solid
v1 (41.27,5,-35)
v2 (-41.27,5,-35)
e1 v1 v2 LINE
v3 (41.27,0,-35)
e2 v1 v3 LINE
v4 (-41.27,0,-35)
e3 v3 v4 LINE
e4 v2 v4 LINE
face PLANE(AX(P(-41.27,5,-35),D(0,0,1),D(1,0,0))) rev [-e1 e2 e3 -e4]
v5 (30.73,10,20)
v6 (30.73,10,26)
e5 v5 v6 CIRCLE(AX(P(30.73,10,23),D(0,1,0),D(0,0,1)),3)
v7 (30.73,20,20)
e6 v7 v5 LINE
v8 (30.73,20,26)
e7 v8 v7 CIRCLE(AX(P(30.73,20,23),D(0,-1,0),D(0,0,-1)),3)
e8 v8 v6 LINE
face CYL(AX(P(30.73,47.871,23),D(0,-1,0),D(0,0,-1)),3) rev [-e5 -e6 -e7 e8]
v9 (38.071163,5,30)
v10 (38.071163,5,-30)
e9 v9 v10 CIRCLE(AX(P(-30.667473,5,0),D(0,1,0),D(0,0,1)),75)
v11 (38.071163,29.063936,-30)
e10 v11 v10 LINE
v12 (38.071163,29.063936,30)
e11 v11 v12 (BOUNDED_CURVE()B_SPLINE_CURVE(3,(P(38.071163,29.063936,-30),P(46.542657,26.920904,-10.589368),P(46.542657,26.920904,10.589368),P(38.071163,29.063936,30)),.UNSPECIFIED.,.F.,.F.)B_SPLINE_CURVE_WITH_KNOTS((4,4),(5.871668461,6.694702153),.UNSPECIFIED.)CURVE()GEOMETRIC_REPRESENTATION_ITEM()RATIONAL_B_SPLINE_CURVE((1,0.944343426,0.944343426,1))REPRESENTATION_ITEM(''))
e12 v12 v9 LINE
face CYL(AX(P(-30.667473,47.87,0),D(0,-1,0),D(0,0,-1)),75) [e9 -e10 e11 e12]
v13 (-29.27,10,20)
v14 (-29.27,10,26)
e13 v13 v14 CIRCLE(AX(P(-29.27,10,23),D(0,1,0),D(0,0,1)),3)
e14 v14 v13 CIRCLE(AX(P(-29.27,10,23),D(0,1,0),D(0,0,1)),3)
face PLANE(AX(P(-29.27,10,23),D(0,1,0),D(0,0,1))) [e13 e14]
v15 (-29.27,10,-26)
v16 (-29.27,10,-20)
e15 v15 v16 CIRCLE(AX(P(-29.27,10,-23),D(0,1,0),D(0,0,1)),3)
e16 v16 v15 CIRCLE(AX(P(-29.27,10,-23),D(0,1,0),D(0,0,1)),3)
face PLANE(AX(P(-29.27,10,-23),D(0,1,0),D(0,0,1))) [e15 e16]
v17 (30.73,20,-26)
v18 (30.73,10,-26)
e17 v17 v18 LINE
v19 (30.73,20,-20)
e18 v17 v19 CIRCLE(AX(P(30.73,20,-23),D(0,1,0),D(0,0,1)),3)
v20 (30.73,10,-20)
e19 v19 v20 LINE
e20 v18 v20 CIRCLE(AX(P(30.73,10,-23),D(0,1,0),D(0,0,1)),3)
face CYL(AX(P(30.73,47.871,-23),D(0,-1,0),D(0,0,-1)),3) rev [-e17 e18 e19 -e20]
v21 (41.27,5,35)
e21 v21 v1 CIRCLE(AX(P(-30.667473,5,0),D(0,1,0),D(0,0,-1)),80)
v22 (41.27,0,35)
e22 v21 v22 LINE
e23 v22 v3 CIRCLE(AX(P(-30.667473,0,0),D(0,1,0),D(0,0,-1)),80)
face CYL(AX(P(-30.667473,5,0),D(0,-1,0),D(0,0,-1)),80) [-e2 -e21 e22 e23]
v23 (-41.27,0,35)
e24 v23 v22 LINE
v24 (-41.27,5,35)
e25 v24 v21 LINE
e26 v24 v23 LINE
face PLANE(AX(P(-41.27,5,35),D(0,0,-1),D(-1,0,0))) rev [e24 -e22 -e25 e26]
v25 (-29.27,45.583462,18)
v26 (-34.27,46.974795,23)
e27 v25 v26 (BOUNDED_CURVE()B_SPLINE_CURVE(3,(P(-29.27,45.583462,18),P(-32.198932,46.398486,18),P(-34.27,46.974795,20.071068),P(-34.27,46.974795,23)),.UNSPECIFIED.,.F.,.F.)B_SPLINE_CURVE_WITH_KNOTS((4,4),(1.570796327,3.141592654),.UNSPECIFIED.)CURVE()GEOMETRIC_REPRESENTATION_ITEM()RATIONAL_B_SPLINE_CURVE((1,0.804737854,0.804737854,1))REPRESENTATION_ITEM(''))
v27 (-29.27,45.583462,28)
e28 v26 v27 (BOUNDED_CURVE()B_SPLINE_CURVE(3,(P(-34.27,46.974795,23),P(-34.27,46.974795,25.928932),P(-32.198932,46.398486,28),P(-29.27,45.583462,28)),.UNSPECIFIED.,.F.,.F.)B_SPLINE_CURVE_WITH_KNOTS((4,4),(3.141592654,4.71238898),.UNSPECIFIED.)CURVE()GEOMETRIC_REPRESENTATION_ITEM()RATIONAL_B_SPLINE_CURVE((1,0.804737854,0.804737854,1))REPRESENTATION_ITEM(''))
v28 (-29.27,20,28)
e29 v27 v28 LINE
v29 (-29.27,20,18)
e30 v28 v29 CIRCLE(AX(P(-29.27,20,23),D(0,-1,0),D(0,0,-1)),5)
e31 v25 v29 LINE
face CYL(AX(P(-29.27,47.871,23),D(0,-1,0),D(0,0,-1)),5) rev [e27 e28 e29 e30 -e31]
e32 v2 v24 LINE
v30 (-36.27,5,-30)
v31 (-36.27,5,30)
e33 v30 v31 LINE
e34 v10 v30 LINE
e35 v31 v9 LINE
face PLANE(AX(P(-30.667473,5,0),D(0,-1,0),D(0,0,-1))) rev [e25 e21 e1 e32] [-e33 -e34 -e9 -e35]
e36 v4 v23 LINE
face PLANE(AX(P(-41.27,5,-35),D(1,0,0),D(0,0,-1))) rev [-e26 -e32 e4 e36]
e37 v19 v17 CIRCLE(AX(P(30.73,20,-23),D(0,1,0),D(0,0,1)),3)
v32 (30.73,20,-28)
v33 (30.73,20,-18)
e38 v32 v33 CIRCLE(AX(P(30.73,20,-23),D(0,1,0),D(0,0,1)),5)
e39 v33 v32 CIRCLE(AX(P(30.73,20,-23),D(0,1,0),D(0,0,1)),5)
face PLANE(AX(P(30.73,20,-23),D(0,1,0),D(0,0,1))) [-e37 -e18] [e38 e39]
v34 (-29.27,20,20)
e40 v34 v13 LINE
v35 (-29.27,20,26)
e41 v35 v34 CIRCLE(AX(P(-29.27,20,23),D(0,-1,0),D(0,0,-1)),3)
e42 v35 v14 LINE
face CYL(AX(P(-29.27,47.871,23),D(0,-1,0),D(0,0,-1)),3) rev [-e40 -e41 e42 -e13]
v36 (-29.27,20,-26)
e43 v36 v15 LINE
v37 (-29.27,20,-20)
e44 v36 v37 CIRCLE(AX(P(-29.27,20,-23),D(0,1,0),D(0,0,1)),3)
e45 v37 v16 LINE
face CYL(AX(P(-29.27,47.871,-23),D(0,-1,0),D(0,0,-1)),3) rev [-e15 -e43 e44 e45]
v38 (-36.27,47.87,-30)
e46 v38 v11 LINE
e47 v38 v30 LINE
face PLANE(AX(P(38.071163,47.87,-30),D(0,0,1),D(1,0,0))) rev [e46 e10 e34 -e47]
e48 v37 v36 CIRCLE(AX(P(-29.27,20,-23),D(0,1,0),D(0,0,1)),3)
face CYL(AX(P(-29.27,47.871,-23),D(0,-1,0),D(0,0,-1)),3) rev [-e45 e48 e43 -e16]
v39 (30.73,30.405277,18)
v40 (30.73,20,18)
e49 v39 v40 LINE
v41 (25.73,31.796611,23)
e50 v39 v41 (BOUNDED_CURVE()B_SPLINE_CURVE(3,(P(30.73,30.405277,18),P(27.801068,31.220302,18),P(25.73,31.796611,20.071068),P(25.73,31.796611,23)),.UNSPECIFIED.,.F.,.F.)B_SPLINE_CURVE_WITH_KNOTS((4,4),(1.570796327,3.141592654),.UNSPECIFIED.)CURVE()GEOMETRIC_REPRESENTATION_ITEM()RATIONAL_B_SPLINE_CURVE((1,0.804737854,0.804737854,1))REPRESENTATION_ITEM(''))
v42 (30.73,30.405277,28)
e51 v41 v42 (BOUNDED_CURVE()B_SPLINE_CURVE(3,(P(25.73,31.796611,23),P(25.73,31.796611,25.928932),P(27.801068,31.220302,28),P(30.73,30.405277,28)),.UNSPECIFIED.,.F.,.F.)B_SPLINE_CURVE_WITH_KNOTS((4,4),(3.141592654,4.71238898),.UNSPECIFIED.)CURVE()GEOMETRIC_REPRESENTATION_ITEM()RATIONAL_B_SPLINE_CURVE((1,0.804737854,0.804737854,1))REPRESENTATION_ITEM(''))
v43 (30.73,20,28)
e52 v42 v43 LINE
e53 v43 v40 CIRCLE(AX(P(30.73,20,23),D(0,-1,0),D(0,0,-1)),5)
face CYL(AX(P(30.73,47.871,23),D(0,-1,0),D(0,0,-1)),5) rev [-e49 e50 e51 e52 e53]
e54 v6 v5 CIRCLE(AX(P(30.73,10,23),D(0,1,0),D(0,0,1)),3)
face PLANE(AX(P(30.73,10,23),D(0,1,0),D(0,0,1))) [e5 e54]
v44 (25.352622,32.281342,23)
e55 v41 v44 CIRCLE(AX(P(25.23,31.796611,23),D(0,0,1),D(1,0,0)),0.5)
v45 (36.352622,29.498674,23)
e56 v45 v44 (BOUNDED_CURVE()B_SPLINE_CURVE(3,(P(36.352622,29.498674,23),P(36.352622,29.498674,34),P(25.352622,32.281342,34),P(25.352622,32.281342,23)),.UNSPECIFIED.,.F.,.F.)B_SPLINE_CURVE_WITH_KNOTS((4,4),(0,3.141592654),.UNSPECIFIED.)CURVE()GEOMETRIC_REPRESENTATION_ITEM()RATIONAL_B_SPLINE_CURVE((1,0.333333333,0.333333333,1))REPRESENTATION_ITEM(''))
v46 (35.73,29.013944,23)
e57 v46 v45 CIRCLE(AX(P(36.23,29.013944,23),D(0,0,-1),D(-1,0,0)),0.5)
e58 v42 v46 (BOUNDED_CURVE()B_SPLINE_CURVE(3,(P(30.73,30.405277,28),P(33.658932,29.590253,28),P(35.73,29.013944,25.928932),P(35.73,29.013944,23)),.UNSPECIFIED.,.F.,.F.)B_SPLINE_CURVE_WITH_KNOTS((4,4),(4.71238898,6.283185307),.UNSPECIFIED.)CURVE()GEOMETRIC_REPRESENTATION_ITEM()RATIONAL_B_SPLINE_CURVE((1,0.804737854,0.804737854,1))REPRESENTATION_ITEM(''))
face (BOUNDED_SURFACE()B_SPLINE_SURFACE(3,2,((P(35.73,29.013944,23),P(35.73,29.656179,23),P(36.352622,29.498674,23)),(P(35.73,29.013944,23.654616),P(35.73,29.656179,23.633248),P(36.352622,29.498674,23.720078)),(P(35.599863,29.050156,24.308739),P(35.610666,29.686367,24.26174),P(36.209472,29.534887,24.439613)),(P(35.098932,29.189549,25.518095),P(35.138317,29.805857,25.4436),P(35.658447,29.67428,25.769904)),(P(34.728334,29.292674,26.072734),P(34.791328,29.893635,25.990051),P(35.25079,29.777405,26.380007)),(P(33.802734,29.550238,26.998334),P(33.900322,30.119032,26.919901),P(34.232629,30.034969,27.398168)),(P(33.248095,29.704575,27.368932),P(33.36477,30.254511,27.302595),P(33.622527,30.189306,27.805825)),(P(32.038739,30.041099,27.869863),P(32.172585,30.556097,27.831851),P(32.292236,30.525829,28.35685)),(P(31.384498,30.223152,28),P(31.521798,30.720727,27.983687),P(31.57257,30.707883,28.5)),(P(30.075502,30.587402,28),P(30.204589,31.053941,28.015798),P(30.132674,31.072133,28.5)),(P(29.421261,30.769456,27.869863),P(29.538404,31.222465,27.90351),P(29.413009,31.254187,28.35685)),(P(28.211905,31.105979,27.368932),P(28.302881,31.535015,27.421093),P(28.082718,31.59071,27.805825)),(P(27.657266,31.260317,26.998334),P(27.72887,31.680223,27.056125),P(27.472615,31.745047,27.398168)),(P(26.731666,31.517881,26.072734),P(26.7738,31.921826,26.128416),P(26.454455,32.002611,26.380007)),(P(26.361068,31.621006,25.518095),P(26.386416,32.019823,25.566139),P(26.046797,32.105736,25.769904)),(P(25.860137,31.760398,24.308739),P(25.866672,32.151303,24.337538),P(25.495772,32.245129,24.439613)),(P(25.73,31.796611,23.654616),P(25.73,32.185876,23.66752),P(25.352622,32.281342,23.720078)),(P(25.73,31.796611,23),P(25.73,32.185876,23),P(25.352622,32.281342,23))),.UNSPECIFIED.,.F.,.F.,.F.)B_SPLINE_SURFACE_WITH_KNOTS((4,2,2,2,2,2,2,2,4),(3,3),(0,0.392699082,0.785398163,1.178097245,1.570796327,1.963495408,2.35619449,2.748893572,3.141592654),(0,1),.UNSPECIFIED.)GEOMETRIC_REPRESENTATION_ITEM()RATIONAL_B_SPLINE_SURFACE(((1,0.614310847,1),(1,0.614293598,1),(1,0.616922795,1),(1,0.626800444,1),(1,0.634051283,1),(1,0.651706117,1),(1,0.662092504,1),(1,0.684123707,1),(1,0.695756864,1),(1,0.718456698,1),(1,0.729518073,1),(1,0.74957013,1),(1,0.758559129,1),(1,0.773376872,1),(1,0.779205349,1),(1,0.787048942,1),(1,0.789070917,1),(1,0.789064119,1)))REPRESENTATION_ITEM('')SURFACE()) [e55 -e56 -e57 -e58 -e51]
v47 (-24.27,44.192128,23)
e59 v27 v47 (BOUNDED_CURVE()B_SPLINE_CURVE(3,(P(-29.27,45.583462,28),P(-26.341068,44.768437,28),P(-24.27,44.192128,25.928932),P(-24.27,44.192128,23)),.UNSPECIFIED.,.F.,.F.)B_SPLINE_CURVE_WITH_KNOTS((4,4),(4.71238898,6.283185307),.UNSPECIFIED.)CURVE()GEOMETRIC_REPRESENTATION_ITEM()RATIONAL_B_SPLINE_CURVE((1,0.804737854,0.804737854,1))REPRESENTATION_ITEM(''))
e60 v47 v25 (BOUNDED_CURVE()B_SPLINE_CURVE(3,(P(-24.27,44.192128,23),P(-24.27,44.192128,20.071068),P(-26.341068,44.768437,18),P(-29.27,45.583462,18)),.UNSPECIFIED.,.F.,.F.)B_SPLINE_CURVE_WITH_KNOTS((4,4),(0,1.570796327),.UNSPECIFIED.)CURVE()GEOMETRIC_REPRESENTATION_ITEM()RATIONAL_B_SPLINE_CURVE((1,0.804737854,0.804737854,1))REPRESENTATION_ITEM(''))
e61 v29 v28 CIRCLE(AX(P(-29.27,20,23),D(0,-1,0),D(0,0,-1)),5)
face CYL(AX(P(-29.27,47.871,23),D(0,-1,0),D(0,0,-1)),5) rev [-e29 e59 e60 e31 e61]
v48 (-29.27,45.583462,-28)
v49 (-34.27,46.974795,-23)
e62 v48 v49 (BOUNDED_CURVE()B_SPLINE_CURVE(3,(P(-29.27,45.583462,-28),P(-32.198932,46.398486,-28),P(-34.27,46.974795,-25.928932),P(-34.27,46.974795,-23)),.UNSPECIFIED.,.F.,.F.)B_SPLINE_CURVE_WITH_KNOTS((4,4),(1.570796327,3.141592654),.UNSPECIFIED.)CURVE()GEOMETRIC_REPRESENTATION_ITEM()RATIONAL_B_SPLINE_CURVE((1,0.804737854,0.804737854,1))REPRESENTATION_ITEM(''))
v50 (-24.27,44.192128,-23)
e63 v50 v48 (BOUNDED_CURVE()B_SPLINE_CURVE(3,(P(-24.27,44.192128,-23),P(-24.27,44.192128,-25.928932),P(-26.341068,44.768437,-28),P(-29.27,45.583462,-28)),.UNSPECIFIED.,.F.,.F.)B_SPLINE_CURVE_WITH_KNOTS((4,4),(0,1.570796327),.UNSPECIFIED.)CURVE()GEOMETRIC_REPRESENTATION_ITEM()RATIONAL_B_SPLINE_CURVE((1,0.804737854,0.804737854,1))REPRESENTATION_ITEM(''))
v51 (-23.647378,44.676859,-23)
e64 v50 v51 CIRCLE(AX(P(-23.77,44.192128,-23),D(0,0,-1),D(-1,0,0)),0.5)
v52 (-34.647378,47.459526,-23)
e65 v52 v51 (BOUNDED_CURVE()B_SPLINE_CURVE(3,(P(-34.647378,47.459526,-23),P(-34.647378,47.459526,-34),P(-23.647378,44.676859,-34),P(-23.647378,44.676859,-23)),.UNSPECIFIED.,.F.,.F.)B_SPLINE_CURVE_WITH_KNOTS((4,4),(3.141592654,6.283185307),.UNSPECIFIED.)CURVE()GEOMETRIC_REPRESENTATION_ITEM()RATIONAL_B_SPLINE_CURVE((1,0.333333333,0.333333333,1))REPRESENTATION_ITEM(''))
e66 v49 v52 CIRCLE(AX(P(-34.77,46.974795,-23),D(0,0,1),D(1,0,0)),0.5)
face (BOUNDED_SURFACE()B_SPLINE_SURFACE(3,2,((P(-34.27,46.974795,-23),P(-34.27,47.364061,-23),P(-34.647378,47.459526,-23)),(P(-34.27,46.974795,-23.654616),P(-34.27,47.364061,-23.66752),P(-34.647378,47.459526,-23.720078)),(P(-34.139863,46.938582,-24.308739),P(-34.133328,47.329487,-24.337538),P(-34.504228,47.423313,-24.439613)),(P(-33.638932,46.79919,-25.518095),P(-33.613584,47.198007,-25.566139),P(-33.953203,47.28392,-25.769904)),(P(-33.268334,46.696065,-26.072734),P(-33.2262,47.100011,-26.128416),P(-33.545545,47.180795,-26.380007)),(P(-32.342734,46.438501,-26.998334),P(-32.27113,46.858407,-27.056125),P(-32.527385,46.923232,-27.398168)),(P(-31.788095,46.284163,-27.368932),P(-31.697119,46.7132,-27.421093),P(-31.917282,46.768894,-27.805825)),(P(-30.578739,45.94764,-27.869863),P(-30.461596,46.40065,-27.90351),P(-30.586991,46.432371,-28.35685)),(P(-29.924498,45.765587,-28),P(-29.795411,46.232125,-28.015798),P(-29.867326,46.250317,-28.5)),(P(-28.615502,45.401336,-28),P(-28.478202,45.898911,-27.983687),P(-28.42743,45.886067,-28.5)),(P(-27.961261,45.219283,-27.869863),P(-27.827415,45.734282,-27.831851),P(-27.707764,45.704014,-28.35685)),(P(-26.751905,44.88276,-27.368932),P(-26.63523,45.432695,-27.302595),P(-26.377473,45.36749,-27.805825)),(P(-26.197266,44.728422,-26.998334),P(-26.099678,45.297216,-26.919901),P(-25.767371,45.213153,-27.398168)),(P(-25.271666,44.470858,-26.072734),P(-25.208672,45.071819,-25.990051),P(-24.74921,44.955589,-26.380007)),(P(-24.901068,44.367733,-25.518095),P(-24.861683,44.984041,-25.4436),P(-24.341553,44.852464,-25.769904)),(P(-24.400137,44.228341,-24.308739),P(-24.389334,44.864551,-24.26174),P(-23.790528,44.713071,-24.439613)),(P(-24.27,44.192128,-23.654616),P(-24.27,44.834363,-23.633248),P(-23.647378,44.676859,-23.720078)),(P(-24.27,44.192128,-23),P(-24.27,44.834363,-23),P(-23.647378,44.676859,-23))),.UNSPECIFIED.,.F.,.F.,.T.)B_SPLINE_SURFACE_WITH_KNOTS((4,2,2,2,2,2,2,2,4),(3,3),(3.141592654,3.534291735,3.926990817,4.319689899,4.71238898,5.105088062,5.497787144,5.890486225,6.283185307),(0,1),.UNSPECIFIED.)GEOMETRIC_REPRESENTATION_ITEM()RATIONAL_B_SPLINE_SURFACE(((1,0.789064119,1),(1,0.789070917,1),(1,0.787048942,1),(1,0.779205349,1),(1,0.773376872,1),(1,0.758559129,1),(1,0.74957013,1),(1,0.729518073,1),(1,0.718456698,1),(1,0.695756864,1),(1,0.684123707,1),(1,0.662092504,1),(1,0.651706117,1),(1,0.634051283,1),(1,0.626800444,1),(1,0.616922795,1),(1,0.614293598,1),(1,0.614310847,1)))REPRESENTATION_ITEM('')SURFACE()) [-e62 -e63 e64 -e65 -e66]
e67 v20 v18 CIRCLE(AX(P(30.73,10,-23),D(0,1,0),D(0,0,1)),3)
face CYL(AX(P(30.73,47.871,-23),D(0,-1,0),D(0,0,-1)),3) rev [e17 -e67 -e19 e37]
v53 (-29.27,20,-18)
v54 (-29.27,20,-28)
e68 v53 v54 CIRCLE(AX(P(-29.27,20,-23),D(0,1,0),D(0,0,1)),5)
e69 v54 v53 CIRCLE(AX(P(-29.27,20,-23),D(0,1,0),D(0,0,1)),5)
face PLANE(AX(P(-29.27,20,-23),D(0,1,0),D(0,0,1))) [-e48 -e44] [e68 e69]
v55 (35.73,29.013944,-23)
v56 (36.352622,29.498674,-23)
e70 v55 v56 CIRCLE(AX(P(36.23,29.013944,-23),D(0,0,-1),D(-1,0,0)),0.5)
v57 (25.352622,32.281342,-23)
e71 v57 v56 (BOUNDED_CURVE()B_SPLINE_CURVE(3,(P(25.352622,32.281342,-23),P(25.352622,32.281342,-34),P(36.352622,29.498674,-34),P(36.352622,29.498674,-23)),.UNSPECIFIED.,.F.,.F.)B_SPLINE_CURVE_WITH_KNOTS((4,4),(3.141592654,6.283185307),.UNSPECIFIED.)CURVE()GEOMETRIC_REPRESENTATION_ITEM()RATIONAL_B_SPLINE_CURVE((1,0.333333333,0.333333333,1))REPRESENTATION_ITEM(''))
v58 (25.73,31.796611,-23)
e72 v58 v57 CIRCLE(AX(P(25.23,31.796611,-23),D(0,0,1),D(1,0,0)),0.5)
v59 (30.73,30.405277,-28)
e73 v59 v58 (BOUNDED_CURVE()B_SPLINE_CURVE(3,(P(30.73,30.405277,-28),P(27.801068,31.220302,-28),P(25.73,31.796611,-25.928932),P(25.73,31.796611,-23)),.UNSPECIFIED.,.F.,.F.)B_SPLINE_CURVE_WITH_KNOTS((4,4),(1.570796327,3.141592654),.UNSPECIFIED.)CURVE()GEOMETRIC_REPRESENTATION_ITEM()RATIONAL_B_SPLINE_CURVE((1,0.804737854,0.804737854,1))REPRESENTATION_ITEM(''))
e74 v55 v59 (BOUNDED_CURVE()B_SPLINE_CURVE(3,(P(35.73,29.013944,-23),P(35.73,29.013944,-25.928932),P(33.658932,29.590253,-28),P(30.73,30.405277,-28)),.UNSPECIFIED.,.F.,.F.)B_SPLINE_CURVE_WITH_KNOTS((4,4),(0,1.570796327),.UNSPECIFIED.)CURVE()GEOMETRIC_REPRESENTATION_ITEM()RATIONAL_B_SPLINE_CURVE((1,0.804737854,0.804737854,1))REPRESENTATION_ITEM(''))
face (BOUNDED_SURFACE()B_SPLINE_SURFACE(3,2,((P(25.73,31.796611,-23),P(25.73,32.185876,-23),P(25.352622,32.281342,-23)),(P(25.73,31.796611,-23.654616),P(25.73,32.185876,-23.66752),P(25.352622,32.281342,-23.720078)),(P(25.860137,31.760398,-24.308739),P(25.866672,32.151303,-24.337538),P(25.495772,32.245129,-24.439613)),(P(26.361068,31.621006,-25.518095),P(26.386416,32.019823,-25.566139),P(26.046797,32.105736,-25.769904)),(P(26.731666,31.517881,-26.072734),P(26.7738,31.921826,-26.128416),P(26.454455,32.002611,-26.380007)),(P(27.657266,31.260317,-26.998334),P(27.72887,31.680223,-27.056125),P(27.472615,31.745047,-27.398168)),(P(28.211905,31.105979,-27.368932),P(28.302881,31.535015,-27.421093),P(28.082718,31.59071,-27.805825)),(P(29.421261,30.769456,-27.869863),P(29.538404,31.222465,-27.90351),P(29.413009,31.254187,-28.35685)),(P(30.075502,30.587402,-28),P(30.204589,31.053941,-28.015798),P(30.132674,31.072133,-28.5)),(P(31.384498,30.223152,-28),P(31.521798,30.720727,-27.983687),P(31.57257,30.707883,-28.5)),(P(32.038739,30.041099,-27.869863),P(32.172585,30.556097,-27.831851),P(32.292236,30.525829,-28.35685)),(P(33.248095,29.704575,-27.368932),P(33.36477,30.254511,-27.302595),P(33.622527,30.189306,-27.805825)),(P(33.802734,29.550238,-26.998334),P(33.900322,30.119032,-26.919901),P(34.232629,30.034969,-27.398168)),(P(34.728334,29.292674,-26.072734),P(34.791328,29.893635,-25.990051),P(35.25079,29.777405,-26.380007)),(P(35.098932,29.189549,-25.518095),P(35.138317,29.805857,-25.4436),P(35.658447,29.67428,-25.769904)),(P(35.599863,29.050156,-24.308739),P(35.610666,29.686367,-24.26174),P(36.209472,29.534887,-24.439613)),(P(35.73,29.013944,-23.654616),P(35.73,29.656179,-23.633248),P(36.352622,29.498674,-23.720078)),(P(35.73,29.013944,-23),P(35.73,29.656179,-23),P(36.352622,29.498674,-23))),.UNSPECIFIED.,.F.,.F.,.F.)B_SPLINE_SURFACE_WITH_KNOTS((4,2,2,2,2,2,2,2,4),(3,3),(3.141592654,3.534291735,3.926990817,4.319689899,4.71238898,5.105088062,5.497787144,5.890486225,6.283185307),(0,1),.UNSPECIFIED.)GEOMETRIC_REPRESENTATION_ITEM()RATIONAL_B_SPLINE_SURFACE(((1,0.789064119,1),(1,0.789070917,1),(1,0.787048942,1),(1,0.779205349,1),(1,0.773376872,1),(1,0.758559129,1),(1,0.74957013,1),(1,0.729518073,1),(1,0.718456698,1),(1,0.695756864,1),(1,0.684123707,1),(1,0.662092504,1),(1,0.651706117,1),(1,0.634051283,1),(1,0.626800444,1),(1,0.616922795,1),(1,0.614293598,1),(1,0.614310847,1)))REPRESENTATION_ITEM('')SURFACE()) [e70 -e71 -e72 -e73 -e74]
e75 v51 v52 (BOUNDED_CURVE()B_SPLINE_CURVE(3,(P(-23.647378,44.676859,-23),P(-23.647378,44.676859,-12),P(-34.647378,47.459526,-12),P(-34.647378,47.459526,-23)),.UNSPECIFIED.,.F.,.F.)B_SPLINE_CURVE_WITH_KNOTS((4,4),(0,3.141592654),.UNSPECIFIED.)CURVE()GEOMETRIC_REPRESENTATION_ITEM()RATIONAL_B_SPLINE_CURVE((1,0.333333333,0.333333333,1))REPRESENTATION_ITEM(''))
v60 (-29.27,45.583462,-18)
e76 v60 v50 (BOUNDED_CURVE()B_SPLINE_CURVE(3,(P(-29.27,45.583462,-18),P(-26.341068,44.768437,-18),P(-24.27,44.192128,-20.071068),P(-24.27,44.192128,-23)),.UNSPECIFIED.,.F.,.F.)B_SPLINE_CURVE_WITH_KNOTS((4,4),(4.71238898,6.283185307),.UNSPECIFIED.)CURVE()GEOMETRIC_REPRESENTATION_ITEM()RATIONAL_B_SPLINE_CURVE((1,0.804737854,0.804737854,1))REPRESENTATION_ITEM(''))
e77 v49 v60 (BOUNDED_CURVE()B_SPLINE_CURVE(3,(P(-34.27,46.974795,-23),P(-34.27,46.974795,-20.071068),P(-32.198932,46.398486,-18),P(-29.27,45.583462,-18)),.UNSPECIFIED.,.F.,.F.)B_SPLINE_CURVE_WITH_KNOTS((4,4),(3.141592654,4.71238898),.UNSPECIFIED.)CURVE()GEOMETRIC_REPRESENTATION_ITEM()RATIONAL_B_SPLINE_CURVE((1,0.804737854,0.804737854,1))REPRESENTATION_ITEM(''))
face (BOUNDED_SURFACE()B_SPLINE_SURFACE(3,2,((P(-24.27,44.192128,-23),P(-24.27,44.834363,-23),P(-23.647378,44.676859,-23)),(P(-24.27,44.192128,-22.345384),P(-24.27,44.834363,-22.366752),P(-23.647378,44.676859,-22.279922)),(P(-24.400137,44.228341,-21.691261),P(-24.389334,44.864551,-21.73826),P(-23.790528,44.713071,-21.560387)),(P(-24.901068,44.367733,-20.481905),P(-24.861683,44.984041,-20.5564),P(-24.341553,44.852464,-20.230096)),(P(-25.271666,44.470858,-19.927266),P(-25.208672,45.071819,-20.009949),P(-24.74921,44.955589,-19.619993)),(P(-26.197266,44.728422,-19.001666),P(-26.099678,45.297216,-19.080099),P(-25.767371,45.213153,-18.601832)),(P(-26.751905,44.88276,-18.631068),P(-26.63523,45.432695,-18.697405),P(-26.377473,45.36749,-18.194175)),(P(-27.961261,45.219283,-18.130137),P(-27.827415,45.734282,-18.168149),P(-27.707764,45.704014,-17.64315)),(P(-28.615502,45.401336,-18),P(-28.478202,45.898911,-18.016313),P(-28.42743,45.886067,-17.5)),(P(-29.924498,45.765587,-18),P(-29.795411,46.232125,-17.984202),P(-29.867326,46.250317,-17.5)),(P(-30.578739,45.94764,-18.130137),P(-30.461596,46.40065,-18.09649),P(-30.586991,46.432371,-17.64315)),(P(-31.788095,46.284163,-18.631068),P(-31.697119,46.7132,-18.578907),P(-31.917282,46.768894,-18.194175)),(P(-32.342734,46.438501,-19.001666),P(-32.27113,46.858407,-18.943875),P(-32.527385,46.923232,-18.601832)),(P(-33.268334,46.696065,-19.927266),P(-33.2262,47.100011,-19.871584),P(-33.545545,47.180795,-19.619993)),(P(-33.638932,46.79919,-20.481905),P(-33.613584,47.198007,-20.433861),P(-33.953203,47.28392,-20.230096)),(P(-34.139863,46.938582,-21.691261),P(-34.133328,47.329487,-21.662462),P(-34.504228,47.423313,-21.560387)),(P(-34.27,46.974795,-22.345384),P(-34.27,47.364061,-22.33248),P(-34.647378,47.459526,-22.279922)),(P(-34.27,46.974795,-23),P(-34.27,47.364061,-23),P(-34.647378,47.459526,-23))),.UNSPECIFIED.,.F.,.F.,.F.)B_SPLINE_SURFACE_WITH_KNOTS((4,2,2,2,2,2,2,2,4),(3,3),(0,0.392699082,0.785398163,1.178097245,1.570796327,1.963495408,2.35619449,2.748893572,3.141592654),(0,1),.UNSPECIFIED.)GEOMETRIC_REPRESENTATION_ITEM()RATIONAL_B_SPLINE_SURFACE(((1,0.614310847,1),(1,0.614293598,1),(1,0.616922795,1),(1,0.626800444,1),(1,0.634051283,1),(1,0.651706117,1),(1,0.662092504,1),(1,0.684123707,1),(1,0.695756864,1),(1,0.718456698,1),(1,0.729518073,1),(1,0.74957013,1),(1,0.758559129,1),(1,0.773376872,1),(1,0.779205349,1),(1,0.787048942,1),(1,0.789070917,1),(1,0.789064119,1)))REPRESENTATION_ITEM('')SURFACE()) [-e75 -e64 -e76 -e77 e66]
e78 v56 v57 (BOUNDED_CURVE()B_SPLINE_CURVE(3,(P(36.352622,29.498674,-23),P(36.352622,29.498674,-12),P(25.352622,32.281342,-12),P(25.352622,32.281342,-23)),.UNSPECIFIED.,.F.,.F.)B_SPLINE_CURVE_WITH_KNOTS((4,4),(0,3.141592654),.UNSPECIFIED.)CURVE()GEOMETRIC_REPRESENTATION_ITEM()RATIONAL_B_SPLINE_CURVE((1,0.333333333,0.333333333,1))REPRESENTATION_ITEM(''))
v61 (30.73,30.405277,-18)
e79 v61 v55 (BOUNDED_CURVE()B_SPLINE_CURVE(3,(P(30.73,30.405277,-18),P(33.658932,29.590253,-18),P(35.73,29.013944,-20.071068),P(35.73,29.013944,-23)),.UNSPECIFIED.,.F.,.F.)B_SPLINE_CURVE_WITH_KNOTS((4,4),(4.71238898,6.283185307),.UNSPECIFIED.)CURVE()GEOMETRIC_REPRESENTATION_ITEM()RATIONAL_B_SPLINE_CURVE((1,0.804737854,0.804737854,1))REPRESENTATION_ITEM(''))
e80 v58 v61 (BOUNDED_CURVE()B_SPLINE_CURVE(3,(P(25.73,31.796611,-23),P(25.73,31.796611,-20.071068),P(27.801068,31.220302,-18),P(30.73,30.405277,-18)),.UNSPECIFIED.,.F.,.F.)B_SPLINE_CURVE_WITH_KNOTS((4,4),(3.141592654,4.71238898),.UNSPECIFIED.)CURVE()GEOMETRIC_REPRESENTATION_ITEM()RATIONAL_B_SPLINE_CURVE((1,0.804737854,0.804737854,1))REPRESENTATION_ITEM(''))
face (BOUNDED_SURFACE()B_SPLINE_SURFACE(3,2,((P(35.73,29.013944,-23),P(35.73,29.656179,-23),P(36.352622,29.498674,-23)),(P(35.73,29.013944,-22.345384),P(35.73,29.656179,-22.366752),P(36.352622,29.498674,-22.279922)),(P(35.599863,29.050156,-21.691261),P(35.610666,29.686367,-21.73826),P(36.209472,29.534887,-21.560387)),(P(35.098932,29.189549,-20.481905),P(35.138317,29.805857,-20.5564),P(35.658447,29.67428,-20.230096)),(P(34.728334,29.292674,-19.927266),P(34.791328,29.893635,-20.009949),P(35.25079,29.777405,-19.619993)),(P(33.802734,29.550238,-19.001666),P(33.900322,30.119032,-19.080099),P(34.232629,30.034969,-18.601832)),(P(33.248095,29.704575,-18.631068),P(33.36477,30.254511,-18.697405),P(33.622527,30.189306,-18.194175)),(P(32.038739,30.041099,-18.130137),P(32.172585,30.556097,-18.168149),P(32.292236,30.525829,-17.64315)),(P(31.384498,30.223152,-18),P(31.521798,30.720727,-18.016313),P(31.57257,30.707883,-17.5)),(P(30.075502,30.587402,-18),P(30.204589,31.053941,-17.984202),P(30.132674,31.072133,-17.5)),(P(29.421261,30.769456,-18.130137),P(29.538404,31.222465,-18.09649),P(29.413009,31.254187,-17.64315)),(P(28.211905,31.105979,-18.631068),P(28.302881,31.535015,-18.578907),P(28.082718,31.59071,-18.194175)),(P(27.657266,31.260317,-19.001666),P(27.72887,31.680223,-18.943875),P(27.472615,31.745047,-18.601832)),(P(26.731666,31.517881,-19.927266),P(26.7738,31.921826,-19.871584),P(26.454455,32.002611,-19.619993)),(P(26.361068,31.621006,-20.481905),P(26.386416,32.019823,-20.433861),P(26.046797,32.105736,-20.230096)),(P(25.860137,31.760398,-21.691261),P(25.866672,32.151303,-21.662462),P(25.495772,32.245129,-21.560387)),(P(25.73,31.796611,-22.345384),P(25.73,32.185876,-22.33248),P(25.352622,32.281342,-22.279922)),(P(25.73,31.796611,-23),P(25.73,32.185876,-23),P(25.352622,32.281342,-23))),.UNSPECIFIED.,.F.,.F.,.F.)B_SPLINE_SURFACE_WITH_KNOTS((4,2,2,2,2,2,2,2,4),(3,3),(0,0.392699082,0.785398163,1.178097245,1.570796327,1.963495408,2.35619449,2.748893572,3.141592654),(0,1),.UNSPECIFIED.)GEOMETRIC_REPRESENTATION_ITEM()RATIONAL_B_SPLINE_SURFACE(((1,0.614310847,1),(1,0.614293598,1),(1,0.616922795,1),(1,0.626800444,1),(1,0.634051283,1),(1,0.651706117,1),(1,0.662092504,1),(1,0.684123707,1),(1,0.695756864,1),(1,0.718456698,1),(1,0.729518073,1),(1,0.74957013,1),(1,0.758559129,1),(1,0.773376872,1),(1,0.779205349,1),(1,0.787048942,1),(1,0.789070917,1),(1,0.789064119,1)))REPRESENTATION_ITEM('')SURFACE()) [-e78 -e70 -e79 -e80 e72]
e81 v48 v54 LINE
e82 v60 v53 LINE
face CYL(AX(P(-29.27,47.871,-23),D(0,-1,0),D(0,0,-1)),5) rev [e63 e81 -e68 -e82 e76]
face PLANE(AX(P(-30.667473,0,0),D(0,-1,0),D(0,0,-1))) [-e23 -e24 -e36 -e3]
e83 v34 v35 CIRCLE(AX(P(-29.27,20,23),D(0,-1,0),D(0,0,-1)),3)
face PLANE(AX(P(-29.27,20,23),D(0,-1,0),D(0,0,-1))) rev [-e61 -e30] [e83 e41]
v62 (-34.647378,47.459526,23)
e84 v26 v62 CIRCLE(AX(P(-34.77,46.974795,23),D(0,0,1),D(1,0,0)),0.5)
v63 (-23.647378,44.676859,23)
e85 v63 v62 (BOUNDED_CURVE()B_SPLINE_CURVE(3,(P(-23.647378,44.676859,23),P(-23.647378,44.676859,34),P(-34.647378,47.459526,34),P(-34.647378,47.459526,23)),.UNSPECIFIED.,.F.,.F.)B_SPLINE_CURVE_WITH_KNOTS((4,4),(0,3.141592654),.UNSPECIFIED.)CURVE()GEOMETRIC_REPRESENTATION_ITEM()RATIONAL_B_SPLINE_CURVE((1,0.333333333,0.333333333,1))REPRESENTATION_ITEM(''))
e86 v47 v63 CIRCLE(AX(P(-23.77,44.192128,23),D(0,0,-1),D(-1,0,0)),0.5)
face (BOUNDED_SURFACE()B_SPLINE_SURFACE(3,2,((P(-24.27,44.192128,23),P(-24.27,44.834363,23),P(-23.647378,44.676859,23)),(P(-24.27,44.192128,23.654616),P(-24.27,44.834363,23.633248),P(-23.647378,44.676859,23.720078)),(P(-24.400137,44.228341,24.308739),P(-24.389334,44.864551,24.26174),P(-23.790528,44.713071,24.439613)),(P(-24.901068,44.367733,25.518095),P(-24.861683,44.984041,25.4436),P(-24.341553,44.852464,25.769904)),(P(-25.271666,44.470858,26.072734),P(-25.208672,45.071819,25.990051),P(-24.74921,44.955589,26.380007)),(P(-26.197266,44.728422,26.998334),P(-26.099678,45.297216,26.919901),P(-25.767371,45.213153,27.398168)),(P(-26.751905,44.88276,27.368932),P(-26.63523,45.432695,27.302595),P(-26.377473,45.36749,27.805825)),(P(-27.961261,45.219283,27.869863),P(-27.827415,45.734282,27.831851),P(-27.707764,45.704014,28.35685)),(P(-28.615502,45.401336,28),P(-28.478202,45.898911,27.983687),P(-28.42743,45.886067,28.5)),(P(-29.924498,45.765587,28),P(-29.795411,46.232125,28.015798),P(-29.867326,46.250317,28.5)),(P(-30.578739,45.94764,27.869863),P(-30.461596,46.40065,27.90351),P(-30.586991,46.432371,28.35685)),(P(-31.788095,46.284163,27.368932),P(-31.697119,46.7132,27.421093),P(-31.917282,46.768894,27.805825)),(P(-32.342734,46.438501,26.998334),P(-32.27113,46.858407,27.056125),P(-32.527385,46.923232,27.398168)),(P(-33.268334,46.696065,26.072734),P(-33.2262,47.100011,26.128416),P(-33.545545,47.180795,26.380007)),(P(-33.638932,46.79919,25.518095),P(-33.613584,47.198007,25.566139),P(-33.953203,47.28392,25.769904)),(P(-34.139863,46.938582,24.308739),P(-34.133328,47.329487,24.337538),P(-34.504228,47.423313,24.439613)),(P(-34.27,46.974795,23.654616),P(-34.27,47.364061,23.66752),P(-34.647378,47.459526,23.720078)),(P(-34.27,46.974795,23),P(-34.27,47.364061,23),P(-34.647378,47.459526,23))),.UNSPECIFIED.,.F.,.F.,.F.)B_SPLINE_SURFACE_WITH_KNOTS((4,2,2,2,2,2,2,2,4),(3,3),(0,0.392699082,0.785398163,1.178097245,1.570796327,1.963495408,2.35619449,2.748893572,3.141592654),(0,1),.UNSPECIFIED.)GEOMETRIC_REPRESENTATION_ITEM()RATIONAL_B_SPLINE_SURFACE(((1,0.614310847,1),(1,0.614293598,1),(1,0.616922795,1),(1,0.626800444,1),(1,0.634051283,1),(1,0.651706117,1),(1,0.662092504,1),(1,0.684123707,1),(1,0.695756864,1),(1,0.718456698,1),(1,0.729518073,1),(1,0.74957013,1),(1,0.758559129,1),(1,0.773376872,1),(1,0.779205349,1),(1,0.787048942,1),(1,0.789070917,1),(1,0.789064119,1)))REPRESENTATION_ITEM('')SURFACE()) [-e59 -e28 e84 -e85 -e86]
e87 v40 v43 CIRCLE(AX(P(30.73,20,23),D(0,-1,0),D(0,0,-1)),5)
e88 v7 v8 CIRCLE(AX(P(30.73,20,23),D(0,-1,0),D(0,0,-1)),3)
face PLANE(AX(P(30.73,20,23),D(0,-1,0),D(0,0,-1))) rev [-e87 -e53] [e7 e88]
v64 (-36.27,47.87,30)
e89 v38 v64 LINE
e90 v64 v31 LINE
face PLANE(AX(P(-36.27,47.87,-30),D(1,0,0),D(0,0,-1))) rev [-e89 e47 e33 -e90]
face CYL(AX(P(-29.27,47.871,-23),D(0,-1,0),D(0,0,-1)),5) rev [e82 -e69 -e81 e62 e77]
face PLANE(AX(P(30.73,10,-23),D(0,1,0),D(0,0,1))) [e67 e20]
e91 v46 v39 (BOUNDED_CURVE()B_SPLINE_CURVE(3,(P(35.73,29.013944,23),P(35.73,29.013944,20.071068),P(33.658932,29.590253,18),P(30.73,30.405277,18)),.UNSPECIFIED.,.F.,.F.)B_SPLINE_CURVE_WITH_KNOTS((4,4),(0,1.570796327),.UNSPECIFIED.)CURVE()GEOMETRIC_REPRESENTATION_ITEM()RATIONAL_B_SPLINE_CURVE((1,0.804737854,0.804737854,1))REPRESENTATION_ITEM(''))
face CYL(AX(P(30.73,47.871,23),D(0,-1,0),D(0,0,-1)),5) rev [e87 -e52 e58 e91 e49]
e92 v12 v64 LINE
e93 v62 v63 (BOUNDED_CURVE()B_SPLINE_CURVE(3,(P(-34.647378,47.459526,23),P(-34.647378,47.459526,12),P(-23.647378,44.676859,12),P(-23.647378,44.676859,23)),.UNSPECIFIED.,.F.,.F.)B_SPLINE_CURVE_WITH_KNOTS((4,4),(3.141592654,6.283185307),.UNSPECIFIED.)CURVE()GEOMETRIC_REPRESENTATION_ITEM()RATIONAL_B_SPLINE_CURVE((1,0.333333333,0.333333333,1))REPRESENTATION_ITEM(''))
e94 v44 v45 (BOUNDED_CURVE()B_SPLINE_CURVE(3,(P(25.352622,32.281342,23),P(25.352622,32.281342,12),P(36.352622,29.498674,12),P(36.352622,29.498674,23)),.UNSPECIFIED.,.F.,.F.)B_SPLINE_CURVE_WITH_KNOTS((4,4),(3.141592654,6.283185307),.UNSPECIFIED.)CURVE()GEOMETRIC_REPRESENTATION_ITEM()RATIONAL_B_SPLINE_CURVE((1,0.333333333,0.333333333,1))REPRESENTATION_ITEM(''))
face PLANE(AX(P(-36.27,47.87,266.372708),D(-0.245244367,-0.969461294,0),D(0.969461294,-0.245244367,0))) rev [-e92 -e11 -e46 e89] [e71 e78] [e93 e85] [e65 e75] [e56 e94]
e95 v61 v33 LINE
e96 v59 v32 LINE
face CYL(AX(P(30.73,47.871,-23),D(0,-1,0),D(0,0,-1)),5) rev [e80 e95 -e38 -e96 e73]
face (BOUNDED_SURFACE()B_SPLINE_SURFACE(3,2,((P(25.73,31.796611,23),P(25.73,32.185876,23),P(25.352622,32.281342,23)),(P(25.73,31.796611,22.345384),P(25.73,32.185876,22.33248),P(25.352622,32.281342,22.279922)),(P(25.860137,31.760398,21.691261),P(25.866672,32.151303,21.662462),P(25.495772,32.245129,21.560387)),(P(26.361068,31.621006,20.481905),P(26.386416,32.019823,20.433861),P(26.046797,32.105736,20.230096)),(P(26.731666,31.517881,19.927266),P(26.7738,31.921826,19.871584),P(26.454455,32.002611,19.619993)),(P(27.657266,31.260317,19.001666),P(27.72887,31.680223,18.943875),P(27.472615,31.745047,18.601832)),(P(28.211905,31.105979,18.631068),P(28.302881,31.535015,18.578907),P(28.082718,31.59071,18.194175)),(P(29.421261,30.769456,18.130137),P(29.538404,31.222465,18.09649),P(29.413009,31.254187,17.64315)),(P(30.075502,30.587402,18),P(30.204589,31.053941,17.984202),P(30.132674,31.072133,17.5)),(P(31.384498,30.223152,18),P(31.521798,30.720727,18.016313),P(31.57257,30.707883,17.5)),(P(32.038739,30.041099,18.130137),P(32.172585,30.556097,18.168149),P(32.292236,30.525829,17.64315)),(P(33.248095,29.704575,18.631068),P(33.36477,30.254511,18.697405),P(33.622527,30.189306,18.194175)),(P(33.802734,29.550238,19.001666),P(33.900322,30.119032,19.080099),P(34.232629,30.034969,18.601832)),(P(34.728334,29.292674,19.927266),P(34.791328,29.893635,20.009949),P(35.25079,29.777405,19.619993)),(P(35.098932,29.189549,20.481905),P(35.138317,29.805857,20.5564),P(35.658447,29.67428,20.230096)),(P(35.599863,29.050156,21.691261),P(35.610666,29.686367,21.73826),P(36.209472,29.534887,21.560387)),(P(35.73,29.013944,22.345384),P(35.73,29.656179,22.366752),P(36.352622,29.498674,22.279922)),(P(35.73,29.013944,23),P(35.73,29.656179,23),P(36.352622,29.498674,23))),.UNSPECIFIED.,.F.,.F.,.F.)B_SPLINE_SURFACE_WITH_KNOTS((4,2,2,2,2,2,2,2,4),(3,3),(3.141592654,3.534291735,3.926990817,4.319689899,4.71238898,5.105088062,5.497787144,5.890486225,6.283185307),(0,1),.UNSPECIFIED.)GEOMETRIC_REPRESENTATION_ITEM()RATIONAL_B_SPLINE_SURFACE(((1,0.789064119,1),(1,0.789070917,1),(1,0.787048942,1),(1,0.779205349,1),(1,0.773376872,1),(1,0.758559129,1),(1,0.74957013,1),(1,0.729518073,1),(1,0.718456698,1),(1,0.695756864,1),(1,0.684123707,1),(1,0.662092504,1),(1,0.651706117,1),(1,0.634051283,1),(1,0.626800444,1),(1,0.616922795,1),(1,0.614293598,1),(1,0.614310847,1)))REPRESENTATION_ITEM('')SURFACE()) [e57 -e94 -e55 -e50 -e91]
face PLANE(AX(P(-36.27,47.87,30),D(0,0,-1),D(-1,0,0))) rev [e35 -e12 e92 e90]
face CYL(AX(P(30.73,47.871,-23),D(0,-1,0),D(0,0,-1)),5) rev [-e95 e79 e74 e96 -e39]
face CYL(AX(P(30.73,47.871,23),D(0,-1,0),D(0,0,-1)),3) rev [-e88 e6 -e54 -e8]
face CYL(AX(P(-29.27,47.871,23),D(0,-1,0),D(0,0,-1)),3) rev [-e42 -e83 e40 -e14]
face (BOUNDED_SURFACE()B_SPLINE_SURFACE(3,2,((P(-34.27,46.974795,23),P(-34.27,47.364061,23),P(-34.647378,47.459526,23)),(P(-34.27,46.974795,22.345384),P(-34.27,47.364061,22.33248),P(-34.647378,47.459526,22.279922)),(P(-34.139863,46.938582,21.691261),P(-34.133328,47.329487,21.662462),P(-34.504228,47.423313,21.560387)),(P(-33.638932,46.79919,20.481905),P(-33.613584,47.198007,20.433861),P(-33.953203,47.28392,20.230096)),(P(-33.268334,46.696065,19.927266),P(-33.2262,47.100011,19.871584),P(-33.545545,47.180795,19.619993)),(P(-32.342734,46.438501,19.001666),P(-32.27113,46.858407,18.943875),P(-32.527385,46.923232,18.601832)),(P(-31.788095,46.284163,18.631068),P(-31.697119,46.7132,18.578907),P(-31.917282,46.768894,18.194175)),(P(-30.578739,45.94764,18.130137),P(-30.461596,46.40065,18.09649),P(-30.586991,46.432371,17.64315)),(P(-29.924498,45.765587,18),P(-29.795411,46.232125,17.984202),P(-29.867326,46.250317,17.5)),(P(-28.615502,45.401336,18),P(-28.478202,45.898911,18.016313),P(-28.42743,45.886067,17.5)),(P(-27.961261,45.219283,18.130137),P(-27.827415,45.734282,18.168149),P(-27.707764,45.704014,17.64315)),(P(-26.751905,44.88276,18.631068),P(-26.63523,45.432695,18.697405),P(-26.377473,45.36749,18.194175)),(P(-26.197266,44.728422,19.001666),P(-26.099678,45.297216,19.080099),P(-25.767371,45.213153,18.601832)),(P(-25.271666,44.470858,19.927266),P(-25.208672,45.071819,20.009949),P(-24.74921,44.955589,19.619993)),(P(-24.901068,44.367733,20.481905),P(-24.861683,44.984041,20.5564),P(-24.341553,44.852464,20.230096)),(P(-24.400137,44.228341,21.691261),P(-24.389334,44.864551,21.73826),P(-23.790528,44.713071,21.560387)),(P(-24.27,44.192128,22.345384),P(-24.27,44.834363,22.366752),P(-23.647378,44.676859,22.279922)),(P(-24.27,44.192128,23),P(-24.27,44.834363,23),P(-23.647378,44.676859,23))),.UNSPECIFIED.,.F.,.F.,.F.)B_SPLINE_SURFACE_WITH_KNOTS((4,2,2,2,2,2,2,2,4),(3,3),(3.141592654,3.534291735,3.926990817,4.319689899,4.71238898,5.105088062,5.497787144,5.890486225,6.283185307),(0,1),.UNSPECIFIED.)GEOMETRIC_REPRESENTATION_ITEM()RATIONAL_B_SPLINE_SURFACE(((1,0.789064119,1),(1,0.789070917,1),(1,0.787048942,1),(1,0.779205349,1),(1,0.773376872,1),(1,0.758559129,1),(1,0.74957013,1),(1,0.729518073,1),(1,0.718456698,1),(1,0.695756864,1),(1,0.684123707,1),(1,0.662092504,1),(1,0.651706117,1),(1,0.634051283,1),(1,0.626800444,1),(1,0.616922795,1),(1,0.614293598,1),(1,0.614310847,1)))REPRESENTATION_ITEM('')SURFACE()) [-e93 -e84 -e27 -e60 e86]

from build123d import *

# Parameters (mm, degrees)
BOSS_EXTRUDE1_DEPTH     = 5
BOSS_EXTRUDE2_DEPTH     = 42.87
CUT_EXTRUDE1_DEPTH      = 95.605682361
CUT_EXTRUDE1_DEPTH_BACK = 95.605682361
CUT_EXTRUDE2_REACH      = 99.138
CUT_EXTRUDE2_START      = -20
SKETCH5_R               = 5
CUT_EXTRUDE3_REACH      = 81.139
CUT_EXTRUDE3_START      = 5
SKETCH6_R               = 3
FILLET1_R               = 0.5


with BuildPart() as part:
    # Sketch1 → Boss-Extrude1 (new body)
    with BuildSketch(Plane(origin=(0, 0, 0), x_dir=(1, 0, 0), z_dir=(0, 1, 0))):
        with BuildLine():
            Line((-41.27, 35), (41.27, 35))
            ThreePointArc((41.27, 35), (49.33252715, 0), (41.27, -35))
            Line((41.27, -35), (-41.27, -35))
            Line((-41.27, -35), (-41.27, 35))
        make_face()
    extrude(amount=BOSS_EXTRUDE1_DEPTH)

    # Sketch2 → Boss-Extrude2 (add)
    with BuildSketch(Plane(origin=(0, 5, 0), x_dir=(1, 0, 0), z_dir=(0, 1, 0))):
        with BuildLine():
            Line((38.071162575, 30), (-36.27, 30))
            Line((-36.27, 30), (-36.27, -30))
            Line((-36.27, -30), (38.071162575, -30))
            ThreePointArc((38.071162575, -30), (44.33252715, 0), (38.071162575, 30))
        make_face()
    extrude(amount=BOSS_EXTRUDE2_DEPTH)

    # Sketch3 → Cut-Extrude1 (cut, two sides: drawn at the far end of the back side and taken through both)
    with BuildSketch(Plane.XY.offset(30).offset(-CUT_EXTRUDE1_DEPTH_BACK)):
        Polygon((44.33252715, -196.474588962), (44.33252715, 5), (44.33252715, 27.48), (-36.27, 47.87), (-36.27, 5), (-36.27, -196.474588962), (-36.27, 206.474588962), (44.33252715, 206.474588962), align=None)
    extrude(amount=CUT_EXTRUDE1_DEPTH + CUT_EXTRUDE1_DEPTH_BACK, mode=Mode.SUBTRACT)

    # Cut-Extrude2: up to this plane
    cut_extrude2_end = Plane(origin=(-36.27, 47.87, 266.372707608), z_dir=(-0.24524436739565725, -0.9694612938434953, 0))
    # Sketch5 → Cut-Extrude2 (cut, up to the surface)
    with BuildSketch(Plane.XZ.offset(CUT_EXTRUDE2_START), mode=Mode.PRIVATE) as cut_extrude2_sk1:
        with Locations(Location((-29.27, 23, 0), (0, 0, 270))):
            Circle(SKETCH5_R)
    cut_extrude2_tool1 = split(extrude(cut_extrude2_sk1.sketch, amount=-CUT_EXTRUDE2_REACH, mode=Mode.PRIVATE), bisect_by=cut_extrude2_end, keep=Keep.BOTH, mode=Mode.PRIVATE)
    add(cut_extrude2_tool1.solids().sort_by_distance((-29.27, 20, 23))[0], mode=Mode.SUBTRACT)
    # Sketch5 → Cut-Extrude2 (cut, up to the surface)
    with BuildSketch(Plane.XZ.offset(CUT_EXTRUDE2_START), mode=Mode.PRIVATE) as cut_extrude2_sk2:
        with Locations(Location((30.73, 23, 0), (0, 0, 270))):
            Circle(SKETCH5_R)
    cut_extrude2_tool2 = split(extrude(cut_extrude2_sk2.sketch, amount=-CUT_EXTRUDE2_REACH, mode=Mode.PRIVATE), bisect_by=cut_extrude2_end, keep=Keep.BOTH, mode=Mode.PRIVATE)
    add(cut_extrude2_tool2.solids().sort_by_distance((30.73, 20, 23))[0], mode=Mode.SUBTRACT)
    # Sketch5 → Cut-Extrude2 (cut, up to the surface)
    with BuildSketch(Plane.XZ.offset(CUT_EXTRUDE2_START), mode=Mode.PRIVATE) as cut_extrude2_sk3:
        with Locations((30.73, -23)):
            Circle(SKETCH5_R)
    cut_extrude2_tool3 = split(extrude(cut_extrude2_sk3.sketch, amount=-CUT_EXTRUDE2_REACH, mode=Mode.PRIVATE), bisect_by=cut_extrude2_end, keep=Keep.BOTH, mode=Mode.PRIVATE)
    add(cut_extrude2_tool3.solids().sort_by_distance((30.73, 20, -23))[0], mode=Mode.SUBTRACT)
    # Sketch5 → Cut-Extrude2 (cut, up to the surface)
    with BuildSketch(Plane.XZ.offset(CUT_EXTRUDE2_START), mode=Mode.PRIVATE) as cut_extrude2_sk4:
        with Locations((-29.27, -23)):
            Circle(SKETCH5_R)
    cut_extrude2_tool4 = split(extrude(cut_extrude2_sk4.sketch, amount=-CUT_EXTRUDE2_REACH, mode=Mode.PRIVATE), bisect_by=cut_extrude2_end, keep=Keep.BOTH, mode=Mode.PRIVATE)
    add(cut_extrude2_tool4.solids().sort_by_distance((-29.27, 20, -23))[0], mode=Mode.SUBTRACT)

    # Sketch6 → Cut-Extrude3 (cut, up to next)
    with BuildSketch(Plane(origin=(0, 5, 0), x_dir=(1, 0, 0), z_dir=(0, 1, 0)).offset(CUT_EXTRUDE3_START), mode=Mode.PRIVATE) as cut_extrude3_sk1:
        with Locations(Location((-29.27, 23, 0), (0, 0, 270))):
            Circle(SKETCH6_R)
    cut_extrude3_tool1 = extrude(cut_extrude3_sk1.sketch, amount=CUT_EXTRUDE3_REACH, mode=Mode.PRIVATE) & part.part
    # Sketch6 → Cut-Extrude3 (cut, up to next)
    with BuildSketch(Plane(origin=(0, 5, 0), x_dir=(1, 0, 0), z_dir=(0, 1, 0)).offset(CUT_EXTRUDE3_START), mode=Mode.PRIVATE) as cut_extrude3_sk2:
        with Locations(Location((30.73, 23, 0), (0, 0, 270))):
            Circle(SKETCH6_R)
    cut_extrude3_tool2 = extrude(cut_extrude3_sk2.sketch, amount=CUT_EXTRUDE3_REACH, mode=Mode.PRIVATE) & part.part
    # Sketch6 → Cut-Extrude3 (cut, up to next)
    with BuildSketch(Plane(origin=(0, 5, 0), x_dir=(1, 0, 0), z_dir=(0, 1, 0)).offset(CUT_EXTRUDE3_START), mode=Mode.PRIVATE) as cut_extrude3_sk3:
        with Locations(Location((-29.27, -23, 0), (0, 0, 90))):
            Circle(SKETCH6_R)
    cut_extrude3_tool3 = extrude(cut_extrude3_sk3.sketch, amount=CUT_EXTRUDE3_REACH, mode=Mode.PRIVATE) & part.part
    # Sketch6 → Cut-Extrude3 (cut, up to next)
    with BuildSketch(Plane(origin=(0, 5, 0), x_dir=(1, 0, 0), z_dir=(0, 1, 0)).offset(CUT_EXTRUDE3_START), mode=Mode.PRIVATE) as cut_extrude3_sk4:
        with Locations(Location((30.73, -23, 0), (0, 0, 90))):
            Circle(SKETCH6_R)
    cut_extrude3_tool4 = extrude(cut_extrude3_sk4.sketch, amount=CUT_EXTRUDE3_REACH, mode=Mode.PRIVATE) & part.part
    add(cut_extrude3_tool1.solids().sort_by_distance((-29.27, 10, -23))[0], mode=Mode.SUBTRACT)
    add(cut_extrude3_tool2.solids().sort_by_distance((30.73, 10, -23))[0], mode=Mode.SUBTRACT)
    add(cut_extrude3_tool3.solids().sort_by_distance((-29.27, 10, 23))[0], mode=Mode.SUBTRACT)
    add(cut_extrude3_tool4.solids().sort_by_distance((30.73, 10, 23))[0], mode=Mode.SUBTRACT)

    # Fillet1
    fillet1_edges = [part.edges().sort_by_distance(p)[0] for p in [
        (30.730000686, 30.921027526, 28),
        (25.73, 32.185876379, -23.000002484),
        (-34.27, 47.364060528, -23.000002484),
        (-29.269999314, 46.099211676, 28),
    ]]
    fillet(fillet1_edges, radius=FILLET1_R)


solid = part.part
